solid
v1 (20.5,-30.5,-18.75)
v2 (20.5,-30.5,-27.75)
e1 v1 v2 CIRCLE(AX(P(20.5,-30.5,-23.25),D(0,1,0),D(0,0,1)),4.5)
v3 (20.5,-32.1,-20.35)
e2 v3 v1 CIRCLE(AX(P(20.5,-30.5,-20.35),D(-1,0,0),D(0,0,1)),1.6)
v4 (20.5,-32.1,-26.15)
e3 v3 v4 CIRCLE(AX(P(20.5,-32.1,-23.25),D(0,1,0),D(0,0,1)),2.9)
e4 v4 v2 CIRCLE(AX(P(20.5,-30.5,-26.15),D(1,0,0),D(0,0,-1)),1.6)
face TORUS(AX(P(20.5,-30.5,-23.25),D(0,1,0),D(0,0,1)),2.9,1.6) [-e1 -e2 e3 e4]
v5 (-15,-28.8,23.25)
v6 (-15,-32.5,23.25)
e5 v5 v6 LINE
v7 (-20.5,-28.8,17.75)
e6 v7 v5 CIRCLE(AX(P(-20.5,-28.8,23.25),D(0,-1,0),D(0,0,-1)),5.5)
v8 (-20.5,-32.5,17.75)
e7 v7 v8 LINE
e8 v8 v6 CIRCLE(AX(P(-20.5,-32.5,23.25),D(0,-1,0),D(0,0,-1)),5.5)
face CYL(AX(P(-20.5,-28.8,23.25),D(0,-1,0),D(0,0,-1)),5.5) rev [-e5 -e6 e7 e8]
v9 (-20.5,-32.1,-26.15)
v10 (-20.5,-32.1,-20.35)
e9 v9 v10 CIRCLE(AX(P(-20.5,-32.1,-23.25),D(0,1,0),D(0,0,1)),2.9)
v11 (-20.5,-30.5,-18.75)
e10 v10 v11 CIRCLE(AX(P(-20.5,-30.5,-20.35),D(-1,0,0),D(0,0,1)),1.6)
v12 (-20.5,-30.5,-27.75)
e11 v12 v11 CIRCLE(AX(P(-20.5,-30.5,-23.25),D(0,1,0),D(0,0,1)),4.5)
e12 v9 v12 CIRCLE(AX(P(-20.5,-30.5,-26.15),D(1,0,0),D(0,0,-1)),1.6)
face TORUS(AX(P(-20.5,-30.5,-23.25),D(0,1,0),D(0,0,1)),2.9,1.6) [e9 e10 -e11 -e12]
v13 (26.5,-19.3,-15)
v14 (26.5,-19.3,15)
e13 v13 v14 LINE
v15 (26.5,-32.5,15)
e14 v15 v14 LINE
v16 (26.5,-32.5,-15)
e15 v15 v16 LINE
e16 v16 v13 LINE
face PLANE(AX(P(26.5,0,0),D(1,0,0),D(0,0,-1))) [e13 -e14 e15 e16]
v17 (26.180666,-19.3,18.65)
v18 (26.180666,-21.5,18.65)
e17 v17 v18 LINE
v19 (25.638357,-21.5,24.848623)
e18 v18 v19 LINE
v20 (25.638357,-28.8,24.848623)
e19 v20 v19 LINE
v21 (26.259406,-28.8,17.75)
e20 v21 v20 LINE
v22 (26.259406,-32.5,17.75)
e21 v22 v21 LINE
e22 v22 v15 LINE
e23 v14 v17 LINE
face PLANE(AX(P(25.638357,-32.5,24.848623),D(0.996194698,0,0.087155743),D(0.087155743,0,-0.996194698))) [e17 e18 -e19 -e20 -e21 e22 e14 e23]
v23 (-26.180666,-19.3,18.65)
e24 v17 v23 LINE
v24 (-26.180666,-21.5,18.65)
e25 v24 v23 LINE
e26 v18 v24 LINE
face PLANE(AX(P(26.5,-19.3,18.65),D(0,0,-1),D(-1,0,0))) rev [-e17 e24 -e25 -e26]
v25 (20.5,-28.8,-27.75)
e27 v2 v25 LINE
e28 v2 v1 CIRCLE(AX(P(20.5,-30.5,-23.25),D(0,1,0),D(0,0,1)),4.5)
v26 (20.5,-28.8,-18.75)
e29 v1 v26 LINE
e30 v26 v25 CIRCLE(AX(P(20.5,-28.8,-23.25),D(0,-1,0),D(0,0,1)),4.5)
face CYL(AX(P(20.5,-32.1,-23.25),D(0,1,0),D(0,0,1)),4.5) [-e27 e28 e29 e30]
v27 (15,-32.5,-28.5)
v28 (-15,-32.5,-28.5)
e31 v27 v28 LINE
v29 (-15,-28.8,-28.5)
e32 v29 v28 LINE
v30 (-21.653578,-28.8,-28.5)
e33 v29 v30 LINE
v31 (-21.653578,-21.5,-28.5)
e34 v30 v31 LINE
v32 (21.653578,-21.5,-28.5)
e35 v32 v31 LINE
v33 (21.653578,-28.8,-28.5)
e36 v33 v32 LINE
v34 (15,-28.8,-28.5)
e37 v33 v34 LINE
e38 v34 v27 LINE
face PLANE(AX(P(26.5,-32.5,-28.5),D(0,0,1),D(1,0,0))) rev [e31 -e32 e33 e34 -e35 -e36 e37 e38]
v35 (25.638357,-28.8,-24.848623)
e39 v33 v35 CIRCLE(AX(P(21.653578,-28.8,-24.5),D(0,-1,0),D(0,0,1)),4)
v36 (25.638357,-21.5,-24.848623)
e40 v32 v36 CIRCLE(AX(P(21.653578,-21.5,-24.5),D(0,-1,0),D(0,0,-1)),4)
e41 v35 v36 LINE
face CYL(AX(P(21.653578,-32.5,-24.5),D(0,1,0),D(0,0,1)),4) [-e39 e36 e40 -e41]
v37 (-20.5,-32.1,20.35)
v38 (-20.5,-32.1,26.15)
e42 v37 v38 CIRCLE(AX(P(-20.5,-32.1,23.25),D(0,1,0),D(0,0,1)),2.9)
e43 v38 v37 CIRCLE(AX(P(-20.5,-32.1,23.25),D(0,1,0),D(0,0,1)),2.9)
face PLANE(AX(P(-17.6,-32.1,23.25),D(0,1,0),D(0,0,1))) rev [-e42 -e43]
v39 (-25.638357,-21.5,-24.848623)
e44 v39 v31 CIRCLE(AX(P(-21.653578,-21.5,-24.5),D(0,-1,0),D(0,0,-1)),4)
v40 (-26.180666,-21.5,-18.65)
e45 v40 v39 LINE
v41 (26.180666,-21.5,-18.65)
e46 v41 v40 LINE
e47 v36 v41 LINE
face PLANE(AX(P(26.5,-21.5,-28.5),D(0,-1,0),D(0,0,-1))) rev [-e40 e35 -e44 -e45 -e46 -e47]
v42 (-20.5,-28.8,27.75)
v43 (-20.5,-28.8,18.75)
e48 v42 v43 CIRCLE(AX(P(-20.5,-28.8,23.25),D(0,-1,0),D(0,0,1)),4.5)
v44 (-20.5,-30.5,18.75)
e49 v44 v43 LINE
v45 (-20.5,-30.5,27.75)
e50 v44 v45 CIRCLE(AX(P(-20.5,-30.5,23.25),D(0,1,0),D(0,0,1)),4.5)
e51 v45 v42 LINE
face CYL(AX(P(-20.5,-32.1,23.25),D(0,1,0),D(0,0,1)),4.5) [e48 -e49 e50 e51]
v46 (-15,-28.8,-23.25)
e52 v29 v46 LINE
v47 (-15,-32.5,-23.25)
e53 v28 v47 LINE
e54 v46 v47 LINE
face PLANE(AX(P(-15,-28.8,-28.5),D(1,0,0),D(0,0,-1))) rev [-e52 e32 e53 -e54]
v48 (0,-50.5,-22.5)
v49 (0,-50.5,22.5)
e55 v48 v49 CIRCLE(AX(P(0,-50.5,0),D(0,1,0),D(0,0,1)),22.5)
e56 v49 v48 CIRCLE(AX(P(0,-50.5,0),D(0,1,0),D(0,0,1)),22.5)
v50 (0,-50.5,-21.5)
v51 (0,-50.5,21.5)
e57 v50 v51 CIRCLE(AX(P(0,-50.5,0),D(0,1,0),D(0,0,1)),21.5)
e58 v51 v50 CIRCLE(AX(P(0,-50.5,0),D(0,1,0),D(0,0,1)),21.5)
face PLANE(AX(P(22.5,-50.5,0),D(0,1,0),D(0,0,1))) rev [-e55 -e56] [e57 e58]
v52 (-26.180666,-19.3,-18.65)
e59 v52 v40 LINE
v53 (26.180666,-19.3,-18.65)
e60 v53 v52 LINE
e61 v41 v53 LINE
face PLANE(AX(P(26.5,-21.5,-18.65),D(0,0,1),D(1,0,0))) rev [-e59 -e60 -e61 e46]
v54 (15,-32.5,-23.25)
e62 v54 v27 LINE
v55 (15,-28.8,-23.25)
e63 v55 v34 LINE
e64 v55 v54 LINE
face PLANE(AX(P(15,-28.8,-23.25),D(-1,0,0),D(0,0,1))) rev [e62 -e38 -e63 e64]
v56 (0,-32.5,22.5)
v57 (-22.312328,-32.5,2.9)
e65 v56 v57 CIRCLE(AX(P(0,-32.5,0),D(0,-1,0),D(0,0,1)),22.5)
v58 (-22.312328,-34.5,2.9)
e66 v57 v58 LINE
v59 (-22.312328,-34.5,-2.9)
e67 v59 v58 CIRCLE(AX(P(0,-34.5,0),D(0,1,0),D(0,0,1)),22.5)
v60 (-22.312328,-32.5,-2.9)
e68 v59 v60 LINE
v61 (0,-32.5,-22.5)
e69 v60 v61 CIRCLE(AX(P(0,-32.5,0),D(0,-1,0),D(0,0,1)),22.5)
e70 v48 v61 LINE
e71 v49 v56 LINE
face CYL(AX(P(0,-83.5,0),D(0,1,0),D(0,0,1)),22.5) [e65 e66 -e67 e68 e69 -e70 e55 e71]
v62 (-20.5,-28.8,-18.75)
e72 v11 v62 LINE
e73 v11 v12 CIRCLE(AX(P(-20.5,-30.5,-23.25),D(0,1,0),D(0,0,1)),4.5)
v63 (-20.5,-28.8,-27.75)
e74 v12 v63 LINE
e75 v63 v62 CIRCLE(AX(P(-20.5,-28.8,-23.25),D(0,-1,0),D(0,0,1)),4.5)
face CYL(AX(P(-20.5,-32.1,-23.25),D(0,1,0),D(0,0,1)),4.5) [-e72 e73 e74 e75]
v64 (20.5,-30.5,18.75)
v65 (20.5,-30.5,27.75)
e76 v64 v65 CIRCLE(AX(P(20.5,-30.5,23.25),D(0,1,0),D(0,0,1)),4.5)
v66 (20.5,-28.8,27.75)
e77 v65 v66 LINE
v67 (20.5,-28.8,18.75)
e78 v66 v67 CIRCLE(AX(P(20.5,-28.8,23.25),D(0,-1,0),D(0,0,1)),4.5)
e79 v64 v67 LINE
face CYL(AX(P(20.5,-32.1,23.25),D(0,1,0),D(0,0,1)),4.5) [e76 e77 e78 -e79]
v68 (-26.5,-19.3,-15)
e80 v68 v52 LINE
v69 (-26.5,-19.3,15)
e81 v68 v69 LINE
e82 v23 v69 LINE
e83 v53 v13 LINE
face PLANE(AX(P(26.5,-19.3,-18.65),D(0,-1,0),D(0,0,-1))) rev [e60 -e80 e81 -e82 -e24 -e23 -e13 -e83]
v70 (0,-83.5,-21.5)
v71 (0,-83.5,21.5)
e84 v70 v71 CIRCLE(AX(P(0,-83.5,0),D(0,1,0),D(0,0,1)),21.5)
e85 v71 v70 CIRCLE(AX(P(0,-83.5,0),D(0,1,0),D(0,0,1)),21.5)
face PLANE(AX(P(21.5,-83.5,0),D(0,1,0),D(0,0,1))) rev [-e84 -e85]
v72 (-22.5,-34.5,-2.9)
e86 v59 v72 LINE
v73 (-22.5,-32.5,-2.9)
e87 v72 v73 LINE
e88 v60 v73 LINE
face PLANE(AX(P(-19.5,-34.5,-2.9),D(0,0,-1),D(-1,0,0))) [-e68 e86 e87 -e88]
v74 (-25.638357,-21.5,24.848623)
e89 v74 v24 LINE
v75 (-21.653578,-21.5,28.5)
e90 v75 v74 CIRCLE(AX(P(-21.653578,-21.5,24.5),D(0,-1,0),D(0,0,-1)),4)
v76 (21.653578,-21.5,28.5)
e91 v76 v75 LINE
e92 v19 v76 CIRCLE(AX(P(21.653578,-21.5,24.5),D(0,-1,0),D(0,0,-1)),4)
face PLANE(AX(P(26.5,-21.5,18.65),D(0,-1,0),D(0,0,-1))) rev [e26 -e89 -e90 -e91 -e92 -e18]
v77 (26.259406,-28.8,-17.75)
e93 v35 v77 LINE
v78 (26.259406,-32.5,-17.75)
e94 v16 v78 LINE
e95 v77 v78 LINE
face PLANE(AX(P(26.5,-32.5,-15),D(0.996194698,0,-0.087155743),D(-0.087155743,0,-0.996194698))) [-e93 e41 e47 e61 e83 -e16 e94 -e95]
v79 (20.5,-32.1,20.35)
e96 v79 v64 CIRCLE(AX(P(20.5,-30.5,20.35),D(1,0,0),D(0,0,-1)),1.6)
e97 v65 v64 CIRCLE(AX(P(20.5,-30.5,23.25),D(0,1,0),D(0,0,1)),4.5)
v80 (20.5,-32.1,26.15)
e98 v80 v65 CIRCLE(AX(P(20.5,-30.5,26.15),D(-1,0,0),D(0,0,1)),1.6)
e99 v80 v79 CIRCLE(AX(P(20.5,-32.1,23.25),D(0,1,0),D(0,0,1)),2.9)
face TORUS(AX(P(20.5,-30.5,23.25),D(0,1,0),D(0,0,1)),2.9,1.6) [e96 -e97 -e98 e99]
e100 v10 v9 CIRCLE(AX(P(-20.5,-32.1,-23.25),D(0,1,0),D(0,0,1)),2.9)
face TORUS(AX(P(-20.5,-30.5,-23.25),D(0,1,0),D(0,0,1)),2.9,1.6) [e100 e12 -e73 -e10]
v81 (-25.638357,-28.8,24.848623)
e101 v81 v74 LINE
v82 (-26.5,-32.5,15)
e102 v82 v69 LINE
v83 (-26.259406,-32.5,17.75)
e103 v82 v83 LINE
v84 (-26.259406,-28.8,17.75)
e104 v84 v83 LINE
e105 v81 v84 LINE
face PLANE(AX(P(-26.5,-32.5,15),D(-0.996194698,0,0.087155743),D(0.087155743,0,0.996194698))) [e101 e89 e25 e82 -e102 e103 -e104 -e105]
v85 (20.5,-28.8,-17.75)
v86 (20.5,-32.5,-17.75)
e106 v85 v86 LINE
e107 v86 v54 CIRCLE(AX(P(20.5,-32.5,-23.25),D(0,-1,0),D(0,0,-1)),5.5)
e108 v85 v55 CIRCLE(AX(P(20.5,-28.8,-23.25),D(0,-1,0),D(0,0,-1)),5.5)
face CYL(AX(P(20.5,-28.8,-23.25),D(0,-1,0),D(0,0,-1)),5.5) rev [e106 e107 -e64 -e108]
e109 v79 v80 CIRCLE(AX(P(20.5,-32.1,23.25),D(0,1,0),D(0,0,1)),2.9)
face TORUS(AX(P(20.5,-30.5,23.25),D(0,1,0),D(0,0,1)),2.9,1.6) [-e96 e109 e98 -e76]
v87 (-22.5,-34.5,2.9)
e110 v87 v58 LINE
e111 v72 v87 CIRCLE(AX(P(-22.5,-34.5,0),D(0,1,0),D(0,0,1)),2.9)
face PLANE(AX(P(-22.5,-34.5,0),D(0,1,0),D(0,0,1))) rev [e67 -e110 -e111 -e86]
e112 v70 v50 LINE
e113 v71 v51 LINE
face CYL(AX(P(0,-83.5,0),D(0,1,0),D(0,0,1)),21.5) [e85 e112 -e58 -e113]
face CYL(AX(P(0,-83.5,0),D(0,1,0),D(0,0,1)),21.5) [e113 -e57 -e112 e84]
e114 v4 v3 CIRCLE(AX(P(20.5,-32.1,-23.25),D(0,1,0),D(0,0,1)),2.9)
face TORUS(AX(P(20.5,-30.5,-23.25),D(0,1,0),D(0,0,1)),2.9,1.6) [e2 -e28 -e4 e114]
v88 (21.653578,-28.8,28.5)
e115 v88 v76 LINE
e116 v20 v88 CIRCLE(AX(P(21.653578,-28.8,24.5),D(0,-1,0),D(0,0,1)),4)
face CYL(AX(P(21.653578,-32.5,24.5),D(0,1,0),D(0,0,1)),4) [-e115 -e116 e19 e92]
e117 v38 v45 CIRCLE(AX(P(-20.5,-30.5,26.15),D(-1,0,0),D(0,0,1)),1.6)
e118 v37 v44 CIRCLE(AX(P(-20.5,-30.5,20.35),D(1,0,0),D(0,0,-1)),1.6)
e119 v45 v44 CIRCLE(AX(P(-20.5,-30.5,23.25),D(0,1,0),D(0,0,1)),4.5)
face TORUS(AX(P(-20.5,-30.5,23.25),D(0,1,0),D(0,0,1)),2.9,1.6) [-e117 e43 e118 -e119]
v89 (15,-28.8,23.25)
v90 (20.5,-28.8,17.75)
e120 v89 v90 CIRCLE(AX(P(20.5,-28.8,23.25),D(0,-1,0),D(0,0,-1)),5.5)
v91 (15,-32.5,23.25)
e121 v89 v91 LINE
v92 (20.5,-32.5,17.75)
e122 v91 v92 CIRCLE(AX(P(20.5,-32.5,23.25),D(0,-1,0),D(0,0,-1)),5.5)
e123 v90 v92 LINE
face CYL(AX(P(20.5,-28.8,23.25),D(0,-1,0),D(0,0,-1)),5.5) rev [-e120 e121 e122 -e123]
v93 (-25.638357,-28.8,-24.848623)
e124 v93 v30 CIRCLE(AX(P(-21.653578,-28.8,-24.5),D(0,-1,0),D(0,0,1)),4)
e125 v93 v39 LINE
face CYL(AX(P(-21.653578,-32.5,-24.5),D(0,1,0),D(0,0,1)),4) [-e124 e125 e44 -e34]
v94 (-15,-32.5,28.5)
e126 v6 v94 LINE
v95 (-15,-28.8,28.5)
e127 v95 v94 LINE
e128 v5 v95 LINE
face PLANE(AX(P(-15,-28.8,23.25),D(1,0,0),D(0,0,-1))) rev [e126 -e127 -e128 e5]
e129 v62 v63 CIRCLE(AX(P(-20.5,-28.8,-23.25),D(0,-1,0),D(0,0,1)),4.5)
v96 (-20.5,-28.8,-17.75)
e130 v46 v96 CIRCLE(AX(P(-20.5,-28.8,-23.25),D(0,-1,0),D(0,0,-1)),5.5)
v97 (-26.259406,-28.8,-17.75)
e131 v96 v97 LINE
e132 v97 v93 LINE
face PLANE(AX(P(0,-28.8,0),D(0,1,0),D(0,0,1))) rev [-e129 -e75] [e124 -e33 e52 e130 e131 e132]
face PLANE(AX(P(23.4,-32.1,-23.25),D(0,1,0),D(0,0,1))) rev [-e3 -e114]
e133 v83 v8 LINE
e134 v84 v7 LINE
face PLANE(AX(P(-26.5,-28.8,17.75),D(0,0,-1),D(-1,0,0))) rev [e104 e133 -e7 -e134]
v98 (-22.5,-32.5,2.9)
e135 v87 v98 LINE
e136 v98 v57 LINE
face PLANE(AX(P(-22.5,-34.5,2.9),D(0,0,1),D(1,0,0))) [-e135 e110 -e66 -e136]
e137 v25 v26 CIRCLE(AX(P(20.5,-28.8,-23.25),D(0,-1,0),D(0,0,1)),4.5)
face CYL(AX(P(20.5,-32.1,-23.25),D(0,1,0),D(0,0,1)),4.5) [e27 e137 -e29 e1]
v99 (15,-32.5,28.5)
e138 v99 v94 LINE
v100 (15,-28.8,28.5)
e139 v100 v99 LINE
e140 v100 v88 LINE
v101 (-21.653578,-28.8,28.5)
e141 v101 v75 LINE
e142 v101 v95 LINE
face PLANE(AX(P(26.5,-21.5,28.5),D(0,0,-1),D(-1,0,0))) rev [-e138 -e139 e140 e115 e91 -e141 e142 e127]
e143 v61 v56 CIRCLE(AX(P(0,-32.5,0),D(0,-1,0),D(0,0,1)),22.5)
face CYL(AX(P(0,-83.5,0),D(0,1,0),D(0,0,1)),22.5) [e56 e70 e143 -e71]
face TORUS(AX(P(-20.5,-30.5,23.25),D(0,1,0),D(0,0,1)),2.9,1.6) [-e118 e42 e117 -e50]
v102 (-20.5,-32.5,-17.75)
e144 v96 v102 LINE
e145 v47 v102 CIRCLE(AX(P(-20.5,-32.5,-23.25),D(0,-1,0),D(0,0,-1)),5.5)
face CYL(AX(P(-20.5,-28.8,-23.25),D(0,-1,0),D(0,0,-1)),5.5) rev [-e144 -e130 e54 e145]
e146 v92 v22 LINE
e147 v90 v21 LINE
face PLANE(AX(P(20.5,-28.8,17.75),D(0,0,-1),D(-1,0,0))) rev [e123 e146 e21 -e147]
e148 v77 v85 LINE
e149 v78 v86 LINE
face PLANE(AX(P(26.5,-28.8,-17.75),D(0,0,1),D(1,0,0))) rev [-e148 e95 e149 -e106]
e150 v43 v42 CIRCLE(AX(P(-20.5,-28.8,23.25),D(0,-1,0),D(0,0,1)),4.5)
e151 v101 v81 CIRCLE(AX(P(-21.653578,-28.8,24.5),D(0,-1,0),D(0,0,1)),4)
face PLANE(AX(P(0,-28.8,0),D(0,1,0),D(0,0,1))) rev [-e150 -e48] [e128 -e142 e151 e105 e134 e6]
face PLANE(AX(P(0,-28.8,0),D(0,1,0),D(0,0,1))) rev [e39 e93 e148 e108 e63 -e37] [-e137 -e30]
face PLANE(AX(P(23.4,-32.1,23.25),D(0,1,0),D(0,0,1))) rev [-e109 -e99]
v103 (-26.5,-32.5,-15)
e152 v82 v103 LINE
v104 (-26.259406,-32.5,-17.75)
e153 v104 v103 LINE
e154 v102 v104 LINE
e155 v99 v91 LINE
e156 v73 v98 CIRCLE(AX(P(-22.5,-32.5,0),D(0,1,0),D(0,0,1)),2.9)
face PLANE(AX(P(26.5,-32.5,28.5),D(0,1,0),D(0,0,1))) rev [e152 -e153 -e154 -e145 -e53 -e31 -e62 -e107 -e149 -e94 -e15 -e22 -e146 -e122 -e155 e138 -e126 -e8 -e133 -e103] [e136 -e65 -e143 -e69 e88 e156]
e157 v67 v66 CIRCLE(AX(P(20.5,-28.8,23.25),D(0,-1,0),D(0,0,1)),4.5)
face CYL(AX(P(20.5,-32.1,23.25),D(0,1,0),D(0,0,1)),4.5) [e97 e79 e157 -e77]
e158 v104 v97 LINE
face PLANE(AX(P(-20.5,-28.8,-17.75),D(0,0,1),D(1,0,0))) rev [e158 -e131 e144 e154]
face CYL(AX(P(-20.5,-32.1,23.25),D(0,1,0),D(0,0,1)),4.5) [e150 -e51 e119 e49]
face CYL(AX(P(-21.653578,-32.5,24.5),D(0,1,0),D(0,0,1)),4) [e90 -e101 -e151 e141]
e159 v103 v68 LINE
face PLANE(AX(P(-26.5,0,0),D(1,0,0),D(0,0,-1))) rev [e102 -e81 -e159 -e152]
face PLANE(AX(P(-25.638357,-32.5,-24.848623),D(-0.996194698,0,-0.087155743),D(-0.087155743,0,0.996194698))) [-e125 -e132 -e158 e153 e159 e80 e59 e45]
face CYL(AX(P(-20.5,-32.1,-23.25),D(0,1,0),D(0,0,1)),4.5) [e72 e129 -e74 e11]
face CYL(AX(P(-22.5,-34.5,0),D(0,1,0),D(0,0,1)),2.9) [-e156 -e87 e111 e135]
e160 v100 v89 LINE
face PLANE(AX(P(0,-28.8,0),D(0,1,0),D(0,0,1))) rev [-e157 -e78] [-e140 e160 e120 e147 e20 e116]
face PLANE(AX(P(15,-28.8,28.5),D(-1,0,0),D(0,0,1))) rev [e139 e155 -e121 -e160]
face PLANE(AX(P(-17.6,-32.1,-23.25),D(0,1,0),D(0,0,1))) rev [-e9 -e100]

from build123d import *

# Parameters (mm, degrees)
EXTRUDE_1_DEPTH             = 26.5
EXTRUDE_1_DEPTH_BACK        = 26.5
SKETCH_2_W                  = 57
SKETCH_2_H                  = 61
CUT_EXTRUDE_1_DEPTH         = 32.5
EXTRUDE_2_DEPTH             = 2
SKETCH_5_W                  = 57
SKETCH_5_H                  = 61
CUT_EXTRUDE_2_DEPTH         = 3.7
PATTERN_LINEAR_1_COUNT      = 2
PATTERN_LINEAR_1_PITCH      = 46.5
PATTERN_LINEAR_1_COUNT_DIR2 = 2
PATTERN_LINEAR_1_PITCH_DIR2 = 41


with BuildPart() as part:
    # 草图1 → 凸台-拉伸1 (new, two sides: drawn at the far end of the back side and taken through both)
    with BuildSketch(Plane(origin=(0, 0, 0), x_dir=(0, 0, -1), z_dir=(1, 0, 0)).offset(-EXTRUDE_1_DEPTH_BACK)):
        Polygon((-28.5, -32.5), (28.5, -32.5), (28.5, -21.5), (18.65, -21.5), (18.65, -19.3), (-18.65, -19.3), (-18.65, -21.5), (-28.5, -21.5), align=None)
    extrude(amount=EXTRUDE_1_DEPTH + EXTRUDE_1_DEPTH_BACK)

    # 草图2 → 切除-拉伸1 (cut)
    with BuildSketch(Plane(origin=(0, 0, 0), x_dir=(1, 0, 0), z_dir=(0, 1, 0))):
        Rectangle(SKETCH_2_W, SKETCH_2_H)
        with BuildLine():
            Line((-26.5, -15), (-25.638357139, -24.848622971))
            ThreePointArc((-25.638357139, -24.848622971), (-24.355939177, -27.449109347), (-21.653578346, -28.5))
            Line((-21.653578346, -28.5), (21.653578346, -28.5))
            ThreePointArc((21.653578346, -28.5), (24.355939177, -27.449109347), (25.638357139, -24.848622971))
            Line((25.638357139, -24.848622971), (26.5, -15))
            Line((26.5, -15), (26.5, 15))
            Line((26.5, 15), (25.638357139, 24.848622971))
            ThreePointArc((25.638357139, 24.848622971), (24.355939177, 27.449109347), (21.653578346, 28.5))
            Line((21.653578346, 28.5), (-21.653578346, 28.5))
            ThreePointArc((-21.653578346, 28.5), (-24.355939177, 27.449109347), (-25.638357139, 24.848622971))
            Line((-25.638357139, 24.848622971), (-26.5, 15))
            Line((-26.5, 15), (-26.5, -15))
        make_face(mode=Mode.SUBTRACT)
    extrude(amount=-CUT_EXTRUDE_1_DEPTH, mode=Mode.SUBTRACT)

    # 草图3 → 旋转1 (revolve)
    with BuildSketch(Plane.XY, mode=Mode.PRIVATE) as revolve_1_sk:
        Polygon((0, -32.5), (22.5, -32.5), (22.5, -50.5), (21.5, -50.5), (21.5, -83.5), (0, -83.5), align=None)
    revolve(revolve_1_sk.sketch.rotate(Axis((0, -83.5, 0), (0, 1, 0)), 270), axis=Axis((0, -83.5, 0), (0, 1, 0)))

    # 草图4 → 凸台-拉伸2 (add)
    with BuildSketch(Plane(origin=(0, -32.5, 0), x_dir=(1, 0, 0), z_dir=(0, 1, 0))):
        with BuildLine():
            Line((-22.5, -2.9), (-19.5, -2.9))
            Line((-19.5, -2.9), (-19.5, 2.9))
            Line((-19.5, 2.9), (-22.5, 2.9))
            ThreePointArc((-22.5, 2.9), (-25.4, 0), (-22.5, -2.9))
        make_face()
    extrude(amount=-EXTRUDE_2_DEPTH)

    # 草图5 → 切除-拉伸2 (cut)
    with BuildSketch(Plane(origin=(0, -32.5, 0), x_dir=(1, 0, 0), z_dir=(0, 1, 0))):
        Rectangle(SKETCH_5_W, SKETCH_5_H)
        with BuildLine():
            Line((-26.5, -17.75), (-20.5, -17.75))
            ThreePointArc((-20.5, -17.75), (-16.610912703, -19.360912703), (-15, -23.25))
            Line((-15, -23.25), (-15, -28.5))
            Line((-15, -28.5), (15, -28.5))
            Line((15, -28.5), (15, -23.25))
            ThreePointArc((15, -23.25), (16.610912703, -19.360912703), (20.5, -17.75))
            Line((20.5, -17.75), (26.5, -17.75))
            Line((26.5, -17.75), (26.5, 17.75))
            Line((26.5, 17.75), (20.5, 17.75))
            ThreePointArc((20.5, 17.75), (16.610912703, 19.360912703), (15, 23.25))
            Line((15, 23.25), (15, 28.5))
            Line((15, 28.5), (-15, 28.5))
            Line((-15, 28.5), (-15, 23.25))
            ThreePointArc((-15, 23.25), (-16.610912703, 19.360912703), (-20.5, 17.75))
            Line((-20.5, 17.75), (-26.5, 17.75))
            Line((-26.5, 17.75), (-26.5, -17.75))
        make_face(mode=Mode.SUBTRACT)
    extrude(amount=CUT_EXTRUDE_2_DEPTH, mode=Mode.SUBTRACT)

    # 草图6 → 旋转2 (revolve)
    with BuildSketch(Plane.XY.offset(23.25), mode=Mode.PRIVATE) as revolve_2_sk:
        with BuildLine():
            Line((20.5, -28.8), (25, -28.8))
            Line((25, -28.8), (25, -30.5))
            ThreePointArc((25, -30.5), (24.53137085, -31.63137085), (23.4, -32.1))
            Line((23.4, -32.1), (20.5, -32.1))
            Line((20.5, -32.1), (20.5, -28.8))
        make_face()
    revolve_2 = revolve(revolve_2_sk.sketch.rotate(Axis((20.5, -32.1, 23.25), (0, 1, 0)), 270), axis=Axis((20.5, -32.1, 23.25), (0, 1, 0)))

    # 阵列(线性)1: Revolve 2 2 × 2
    with Locations(*[(-j * PATTERN_LINEAR_1_PITCH_DIR2, 0, -i * PATTERN_LINEAR_1_PITCH) for i in range(PATTERN_LINEAR_1_COUNT) for j in range(PATTERN_LINEAR_1_COUNT_DIR2) if (i, j) != (0, 0)]):
        add(revolve_2)


solid = part.part
